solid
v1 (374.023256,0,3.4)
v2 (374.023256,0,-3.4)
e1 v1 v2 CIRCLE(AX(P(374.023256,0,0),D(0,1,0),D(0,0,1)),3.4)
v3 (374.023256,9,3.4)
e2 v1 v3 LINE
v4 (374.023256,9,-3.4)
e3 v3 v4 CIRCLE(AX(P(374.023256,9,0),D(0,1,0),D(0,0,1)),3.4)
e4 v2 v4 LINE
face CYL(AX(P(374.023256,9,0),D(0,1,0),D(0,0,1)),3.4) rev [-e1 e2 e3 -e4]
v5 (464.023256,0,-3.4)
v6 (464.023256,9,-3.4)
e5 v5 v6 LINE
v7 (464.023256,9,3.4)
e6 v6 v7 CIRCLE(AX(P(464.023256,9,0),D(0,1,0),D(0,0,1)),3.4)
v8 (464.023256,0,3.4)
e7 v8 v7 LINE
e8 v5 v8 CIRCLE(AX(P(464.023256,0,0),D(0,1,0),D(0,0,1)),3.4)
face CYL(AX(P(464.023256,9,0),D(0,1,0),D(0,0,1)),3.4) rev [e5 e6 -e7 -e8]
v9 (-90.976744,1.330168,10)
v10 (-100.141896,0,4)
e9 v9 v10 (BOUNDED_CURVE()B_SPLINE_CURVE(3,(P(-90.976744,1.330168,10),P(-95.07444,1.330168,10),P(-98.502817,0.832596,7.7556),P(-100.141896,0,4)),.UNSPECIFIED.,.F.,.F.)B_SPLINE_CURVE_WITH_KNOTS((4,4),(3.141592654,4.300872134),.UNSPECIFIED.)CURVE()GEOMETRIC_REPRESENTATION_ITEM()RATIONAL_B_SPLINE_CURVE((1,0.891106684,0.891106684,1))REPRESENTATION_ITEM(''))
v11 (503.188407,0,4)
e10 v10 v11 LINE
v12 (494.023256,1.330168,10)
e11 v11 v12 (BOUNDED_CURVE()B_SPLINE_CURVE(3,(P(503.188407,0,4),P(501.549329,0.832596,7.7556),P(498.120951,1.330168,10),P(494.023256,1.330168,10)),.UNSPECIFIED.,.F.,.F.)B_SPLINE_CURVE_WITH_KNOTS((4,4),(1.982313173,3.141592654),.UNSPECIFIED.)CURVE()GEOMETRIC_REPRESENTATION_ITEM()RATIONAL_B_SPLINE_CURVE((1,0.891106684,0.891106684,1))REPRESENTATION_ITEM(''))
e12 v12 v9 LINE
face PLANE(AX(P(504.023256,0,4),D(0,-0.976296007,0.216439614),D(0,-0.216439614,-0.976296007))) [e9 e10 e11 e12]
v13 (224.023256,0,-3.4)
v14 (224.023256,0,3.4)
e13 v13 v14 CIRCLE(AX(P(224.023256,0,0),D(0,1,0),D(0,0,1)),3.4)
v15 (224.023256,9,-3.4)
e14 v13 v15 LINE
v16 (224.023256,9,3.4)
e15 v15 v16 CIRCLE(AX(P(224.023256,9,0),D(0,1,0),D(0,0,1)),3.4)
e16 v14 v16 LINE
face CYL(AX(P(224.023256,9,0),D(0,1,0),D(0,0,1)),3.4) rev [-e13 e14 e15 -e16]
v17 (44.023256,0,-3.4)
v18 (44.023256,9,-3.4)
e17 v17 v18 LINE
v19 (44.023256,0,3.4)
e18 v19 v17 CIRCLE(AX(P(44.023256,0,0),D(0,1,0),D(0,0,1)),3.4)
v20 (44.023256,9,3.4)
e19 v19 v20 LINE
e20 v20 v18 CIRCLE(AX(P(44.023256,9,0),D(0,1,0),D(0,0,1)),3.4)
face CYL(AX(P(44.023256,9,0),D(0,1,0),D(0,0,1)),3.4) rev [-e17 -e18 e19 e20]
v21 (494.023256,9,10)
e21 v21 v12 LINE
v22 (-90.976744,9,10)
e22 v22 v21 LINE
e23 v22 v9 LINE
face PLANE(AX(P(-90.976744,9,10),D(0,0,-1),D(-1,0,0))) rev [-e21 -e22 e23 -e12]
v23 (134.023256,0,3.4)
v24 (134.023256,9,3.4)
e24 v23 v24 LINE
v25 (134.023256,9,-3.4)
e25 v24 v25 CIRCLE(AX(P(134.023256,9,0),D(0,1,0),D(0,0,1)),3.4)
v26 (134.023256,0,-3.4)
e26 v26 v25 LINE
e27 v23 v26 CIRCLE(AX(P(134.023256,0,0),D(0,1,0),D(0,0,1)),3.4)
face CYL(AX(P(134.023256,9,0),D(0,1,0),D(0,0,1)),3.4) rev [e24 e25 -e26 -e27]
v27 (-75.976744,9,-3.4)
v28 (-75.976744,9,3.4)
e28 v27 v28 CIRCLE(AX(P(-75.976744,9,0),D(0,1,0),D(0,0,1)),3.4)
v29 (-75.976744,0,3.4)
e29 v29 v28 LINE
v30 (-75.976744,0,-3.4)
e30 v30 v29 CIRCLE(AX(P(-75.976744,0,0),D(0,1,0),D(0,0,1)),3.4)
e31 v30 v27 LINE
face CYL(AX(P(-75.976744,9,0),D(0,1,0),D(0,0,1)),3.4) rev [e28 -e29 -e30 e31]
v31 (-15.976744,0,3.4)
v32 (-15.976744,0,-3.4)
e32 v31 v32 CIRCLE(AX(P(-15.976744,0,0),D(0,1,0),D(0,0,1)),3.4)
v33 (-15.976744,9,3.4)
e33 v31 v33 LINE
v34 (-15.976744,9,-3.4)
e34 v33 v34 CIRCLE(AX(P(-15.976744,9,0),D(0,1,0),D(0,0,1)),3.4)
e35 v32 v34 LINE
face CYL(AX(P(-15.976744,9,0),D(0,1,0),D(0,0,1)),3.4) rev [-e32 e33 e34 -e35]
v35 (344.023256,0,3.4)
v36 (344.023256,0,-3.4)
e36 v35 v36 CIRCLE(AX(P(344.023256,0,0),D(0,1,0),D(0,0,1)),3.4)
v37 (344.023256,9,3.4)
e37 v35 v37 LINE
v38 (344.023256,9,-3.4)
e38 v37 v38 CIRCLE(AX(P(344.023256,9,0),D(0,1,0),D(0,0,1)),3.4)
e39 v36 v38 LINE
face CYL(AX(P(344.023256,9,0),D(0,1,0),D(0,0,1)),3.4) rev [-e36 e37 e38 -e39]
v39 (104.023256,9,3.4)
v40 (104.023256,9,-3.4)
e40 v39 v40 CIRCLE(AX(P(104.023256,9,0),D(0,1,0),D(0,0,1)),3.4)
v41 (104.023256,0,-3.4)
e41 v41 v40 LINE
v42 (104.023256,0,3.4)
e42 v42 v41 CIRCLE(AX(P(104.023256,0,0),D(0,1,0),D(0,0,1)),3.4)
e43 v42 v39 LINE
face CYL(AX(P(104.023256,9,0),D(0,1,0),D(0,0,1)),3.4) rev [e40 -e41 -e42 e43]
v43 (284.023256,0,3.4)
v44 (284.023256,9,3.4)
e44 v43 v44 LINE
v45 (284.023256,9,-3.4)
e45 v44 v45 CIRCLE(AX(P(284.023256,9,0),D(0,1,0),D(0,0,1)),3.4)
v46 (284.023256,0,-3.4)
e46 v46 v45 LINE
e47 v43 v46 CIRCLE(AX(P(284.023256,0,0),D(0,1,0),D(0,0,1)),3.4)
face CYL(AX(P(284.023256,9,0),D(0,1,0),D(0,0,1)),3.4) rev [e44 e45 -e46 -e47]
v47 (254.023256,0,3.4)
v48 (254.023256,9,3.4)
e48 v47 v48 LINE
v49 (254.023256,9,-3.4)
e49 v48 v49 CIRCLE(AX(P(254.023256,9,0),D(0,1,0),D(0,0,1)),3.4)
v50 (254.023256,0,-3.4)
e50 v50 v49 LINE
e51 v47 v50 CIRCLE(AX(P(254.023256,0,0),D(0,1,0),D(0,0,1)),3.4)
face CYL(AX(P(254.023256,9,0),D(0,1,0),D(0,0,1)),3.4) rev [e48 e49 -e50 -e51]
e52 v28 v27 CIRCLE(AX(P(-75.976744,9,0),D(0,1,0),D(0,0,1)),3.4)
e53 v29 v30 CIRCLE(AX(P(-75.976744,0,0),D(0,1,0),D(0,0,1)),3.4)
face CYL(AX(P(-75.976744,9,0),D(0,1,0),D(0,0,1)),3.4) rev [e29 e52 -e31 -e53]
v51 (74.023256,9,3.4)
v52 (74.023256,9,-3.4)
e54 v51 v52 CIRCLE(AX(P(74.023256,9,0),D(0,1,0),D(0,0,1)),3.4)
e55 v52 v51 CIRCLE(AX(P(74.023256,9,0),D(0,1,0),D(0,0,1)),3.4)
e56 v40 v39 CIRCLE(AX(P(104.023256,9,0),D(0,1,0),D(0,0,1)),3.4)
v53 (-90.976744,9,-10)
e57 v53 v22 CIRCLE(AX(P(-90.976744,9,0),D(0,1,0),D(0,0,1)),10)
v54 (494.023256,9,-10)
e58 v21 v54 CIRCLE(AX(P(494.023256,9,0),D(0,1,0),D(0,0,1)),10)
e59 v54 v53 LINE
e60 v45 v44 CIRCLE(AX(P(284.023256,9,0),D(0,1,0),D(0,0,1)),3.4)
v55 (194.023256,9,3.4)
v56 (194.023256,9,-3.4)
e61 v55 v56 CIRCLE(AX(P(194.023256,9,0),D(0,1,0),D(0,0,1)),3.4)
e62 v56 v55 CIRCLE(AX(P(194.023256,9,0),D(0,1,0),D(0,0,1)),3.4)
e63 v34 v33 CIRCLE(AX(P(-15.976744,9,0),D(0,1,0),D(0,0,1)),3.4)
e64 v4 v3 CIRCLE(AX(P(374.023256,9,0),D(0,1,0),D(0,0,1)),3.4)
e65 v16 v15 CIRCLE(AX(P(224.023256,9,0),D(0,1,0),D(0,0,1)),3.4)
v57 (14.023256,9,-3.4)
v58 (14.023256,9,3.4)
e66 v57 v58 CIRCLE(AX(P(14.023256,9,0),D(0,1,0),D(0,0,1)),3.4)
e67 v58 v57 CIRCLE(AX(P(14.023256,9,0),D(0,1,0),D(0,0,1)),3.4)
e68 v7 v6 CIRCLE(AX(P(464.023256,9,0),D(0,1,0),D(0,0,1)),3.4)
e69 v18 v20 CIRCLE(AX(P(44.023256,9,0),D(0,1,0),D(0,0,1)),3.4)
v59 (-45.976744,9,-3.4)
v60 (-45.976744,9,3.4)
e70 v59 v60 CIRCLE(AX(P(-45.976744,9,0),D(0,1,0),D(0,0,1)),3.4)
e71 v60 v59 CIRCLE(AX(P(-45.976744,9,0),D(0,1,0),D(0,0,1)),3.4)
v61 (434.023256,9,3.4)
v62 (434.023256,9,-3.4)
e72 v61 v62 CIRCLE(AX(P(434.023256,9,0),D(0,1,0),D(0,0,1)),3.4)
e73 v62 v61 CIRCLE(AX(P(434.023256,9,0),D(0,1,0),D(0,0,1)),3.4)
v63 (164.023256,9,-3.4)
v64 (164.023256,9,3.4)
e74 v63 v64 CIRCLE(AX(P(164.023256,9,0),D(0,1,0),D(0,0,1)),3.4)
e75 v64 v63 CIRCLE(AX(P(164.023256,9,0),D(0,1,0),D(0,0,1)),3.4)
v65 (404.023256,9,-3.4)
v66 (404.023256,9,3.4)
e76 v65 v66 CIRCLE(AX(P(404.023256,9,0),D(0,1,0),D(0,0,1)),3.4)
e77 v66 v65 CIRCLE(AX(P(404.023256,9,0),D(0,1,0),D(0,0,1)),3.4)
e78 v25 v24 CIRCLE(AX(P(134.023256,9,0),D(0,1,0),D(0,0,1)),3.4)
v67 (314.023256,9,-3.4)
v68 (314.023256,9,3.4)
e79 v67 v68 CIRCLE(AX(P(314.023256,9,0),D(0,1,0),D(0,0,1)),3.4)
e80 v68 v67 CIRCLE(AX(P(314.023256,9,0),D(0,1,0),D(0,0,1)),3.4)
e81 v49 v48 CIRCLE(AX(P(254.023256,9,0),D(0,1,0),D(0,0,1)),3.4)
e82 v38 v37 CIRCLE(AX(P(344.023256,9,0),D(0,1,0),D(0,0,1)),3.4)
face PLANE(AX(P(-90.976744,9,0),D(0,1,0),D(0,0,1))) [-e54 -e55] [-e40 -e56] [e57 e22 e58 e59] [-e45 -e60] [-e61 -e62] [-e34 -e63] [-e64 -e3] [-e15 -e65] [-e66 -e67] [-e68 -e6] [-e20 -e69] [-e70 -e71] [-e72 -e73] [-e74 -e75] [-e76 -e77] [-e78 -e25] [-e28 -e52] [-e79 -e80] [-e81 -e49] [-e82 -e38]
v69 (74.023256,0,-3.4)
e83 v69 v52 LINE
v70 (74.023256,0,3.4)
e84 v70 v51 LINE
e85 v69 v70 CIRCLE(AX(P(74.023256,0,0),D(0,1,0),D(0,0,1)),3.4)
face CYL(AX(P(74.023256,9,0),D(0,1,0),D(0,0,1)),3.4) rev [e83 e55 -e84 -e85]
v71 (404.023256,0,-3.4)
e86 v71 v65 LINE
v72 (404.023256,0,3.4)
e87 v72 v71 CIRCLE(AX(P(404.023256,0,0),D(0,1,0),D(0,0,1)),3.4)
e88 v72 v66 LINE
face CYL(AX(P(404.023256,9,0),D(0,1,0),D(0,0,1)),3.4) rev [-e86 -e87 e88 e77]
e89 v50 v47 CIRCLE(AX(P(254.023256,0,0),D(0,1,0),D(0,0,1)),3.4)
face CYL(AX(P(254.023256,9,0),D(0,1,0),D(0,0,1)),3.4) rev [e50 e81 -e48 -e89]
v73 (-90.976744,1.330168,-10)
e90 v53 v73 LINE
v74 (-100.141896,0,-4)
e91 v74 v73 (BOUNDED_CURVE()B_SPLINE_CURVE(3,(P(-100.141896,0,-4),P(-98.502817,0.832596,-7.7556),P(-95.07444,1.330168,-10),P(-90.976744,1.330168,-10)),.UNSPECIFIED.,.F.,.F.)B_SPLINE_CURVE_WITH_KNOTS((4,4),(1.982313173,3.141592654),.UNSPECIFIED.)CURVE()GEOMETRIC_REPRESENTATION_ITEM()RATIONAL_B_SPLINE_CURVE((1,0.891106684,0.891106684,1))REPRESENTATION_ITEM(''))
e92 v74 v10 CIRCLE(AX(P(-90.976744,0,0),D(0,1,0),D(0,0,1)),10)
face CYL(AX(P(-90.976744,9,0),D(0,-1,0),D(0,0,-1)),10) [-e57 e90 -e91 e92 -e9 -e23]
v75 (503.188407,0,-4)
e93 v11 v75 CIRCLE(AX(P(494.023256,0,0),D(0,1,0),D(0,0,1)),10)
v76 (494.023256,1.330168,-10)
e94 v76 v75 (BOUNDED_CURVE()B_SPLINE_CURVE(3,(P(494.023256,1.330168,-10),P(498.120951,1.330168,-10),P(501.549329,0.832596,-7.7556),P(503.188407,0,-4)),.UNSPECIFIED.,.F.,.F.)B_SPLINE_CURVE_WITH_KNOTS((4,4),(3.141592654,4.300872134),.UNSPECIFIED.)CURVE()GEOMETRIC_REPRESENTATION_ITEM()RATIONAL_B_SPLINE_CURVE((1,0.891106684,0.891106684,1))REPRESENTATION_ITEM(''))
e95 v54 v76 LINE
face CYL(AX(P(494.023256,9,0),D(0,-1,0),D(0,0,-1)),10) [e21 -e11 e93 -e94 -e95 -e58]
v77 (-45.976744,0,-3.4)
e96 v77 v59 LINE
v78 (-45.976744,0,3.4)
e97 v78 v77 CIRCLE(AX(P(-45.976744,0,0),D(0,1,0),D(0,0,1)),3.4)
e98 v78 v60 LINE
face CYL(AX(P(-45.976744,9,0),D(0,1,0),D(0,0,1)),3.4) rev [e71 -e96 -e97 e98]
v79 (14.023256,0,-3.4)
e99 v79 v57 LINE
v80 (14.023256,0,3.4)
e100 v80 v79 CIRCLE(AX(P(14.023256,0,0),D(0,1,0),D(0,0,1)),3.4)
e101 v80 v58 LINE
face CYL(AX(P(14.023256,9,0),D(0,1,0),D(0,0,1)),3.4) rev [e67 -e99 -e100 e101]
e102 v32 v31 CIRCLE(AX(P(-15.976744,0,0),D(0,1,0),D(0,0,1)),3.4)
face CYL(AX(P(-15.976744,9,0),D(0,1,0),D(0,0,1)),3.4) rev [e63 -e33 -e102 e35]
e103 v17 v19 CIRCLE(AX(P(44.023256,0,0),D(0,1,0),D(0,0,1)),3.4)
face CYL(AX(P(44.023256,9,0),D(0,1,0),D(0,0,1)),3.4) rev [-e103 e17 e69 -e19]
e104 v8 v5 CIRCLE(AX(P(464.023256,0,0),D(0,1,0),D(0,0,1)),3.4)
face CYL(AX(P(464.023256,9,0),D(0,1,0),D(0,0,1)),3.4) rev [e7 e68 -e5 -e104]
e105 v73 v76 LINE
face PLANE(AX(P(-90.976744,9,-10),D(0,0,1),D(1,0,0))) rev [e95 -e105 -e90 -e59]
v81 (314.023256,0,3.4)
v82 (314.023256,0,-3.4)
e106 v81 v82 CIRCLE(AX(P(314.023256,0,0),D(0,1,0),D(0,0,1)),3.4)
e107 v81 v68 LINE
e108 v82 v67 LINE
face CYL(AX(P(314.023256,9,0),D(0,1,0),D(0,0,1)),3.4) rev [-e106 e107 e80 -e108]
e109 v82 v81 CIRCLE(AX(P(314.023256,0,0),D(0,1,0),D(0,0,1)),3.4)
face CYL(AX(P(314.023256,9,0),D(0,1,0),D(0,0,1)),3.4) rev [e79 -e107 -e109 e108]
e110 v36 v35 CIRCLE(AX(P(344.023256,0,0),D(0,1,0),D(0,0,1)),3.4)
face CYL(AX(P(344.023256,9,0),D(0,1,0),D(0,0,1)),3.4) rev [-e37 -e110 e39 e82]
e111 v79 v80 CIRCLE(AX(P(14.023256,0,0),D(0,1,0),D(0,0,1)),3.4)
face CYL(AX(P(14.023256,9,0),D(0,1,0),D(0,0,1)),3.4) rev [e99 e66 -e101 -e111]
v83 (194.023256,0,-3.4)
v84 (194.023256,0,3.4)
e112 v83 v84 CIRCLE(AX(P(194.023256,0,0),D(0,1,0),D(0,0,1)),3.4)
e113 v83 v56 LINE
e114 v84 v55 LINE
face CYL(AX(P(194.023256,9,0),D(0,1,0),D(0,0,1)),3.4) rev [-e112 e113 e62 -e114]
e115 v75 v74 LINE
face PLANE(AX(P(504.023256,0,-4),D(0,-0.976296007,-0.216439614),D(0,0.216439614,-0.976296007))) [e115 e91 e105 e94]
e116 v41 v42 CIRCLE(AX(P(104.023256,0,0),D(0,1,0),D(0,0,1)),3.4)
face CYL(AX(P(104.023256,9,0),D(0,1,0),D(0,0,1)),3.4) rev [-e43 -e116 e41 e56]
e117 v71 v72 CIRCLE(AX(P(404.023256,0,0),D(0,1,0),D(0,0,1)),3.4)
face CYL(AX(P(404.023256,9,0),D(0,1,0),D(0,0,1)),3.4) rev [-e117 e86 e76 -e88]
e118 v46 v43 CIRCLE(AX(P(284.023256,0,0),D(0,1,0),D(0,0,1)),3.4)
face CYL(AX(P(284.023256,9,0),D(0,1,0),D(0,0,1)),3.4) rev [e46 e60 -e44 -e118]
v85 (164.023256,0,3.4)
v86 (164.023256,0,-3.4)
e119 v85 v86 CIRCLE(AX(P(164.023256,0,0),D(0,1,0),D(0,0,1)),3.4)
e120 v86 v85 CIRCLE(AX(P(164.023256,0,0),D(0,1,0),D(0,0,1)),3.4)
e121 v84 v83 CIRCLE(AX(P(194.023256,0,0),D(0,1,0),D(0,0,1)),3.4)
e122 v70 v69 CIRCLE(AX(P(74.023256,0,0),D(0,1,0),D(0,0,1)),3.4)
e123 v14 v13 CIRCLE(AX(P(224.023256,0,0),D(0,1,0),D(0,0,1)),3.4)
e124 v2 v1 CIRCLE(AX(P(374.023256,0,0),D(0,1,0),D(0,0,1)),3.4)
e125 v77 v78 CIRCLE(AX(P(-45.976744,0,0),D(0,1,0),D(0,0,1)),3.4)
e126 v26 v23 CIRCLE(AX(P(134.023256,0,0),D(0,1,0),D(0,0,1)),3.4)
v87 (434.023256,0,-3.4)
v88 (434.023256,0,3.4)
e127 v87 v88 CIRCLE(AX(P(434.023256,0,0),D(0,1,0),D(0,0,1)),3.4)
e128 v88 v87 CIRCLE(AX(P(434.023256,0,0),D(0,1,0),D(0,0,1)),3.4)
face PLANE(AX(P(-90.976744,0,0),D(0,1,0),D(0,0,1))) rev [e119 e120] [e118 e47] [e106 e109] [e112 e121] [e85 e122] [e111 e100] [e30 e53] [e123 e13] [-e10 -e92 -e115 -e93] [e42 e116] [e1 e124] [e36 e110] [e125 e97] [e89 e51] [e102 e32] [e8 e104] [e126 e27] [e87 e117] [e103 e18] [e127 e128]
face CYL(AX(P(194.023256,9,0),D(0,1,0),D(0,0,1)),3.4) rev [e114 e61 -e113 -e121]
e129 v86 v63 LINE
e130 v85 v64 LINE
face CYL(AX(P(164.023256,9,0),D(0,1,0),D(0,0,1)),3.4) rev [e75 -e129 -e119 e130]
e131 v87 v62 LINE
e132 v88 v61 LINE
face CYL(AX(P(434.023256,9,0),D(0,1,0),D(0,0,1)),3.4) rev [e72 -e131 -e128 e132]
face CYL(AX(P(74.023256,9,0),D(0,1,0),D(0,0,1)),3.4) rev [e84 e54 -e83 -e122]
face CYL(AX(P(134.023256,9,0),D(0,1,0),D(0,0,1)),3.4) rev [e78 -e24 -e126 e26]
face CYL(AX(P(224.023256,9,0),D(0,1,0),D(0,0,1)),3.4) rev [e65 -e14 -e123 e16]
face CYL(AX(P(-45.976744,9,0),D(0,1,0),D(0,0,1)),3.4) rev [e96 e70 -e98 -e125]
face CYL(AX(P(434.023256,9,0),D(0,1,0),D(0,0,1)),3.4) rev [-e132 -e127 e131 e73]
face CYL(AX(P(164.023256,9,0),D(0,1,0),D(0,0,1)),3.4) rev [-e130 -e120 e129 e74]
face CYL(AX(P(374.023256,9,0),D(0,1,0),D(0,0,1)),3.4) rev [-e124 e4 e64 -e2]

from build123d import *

# Parameters (mm, degrees)
BOSS_EXTRUDE1_DEPTH = 9
M8_TAPPED_HOLE1_D   = 6.8
LPATTERN1_COUNT     = 19
LPATTERN1_PITCH     = 30
CUT_EXTRUDE1_START  = -200
CUT_EXTRUDE1_DEPTH  = 705.20277905


with BuildPart() as part:
    # Sketch1 → Boss-Extrude1 (new body)
    with BuildSketch(Plane(origin=(0, 0, 0), x_dir=(1, 0, 0), z_dir=(0, 1, 0))):
        with BuildLine():
            Line((-90.976744186, 10), (494.023255814, 10))
            ThreePointArc((494.023255814, 10), (504.023255814, 0), (494.023255814, -10))
            Line((494.023255814, -10), (-90.976744186, -10))
            ThreePointArc((-90.976744186, -10), (-100.976744186, 0), (-90.976744186, 10))
        make_face()
    extrude(amount=BOSS_EXTRUDE1_DEPTH)

    # M8 Tapped Hole1 (through all)
    with Locations(Plane(origin=(0, 9, 0), x_dir=(1, 0, 0), z_dir=(0, 1, 0))):
        with Locations((-75.976744186, 0)):
            m8_tapped_hole1 = Hole(M8_TAPPED_HOLE1_D / 2)

    # LPattern1: M8 Tapped Hole1 ×19
    with Locations(*[(i * LPATTERN1_PITCH, 0, 0) for i in range(1, LPATTERN1_COUNT)]):
        add(m8_tapped_hole1, mode=Mode.SUBTRACT)

    # Sketch4 → Cut-Extrude1 (cut, through all)
    with BuildSketch(Plane(origin=(0, 0, 0), x_dir=(0, 0, -1), z_dir=(1, 0, 0)).offset(CUT_EXTRUDE1_START)):
        Polygon((4, 0), (14, 0), (14, 2.216946626), align=None)
        Polygon((-14, 2.216946626), (-14, 0), (-4, 0), align=None)
    extrude(amount=CUT_EXTRUDE1_DEPTH, mode=Mode.SUBTRACT)


solid = part.part
